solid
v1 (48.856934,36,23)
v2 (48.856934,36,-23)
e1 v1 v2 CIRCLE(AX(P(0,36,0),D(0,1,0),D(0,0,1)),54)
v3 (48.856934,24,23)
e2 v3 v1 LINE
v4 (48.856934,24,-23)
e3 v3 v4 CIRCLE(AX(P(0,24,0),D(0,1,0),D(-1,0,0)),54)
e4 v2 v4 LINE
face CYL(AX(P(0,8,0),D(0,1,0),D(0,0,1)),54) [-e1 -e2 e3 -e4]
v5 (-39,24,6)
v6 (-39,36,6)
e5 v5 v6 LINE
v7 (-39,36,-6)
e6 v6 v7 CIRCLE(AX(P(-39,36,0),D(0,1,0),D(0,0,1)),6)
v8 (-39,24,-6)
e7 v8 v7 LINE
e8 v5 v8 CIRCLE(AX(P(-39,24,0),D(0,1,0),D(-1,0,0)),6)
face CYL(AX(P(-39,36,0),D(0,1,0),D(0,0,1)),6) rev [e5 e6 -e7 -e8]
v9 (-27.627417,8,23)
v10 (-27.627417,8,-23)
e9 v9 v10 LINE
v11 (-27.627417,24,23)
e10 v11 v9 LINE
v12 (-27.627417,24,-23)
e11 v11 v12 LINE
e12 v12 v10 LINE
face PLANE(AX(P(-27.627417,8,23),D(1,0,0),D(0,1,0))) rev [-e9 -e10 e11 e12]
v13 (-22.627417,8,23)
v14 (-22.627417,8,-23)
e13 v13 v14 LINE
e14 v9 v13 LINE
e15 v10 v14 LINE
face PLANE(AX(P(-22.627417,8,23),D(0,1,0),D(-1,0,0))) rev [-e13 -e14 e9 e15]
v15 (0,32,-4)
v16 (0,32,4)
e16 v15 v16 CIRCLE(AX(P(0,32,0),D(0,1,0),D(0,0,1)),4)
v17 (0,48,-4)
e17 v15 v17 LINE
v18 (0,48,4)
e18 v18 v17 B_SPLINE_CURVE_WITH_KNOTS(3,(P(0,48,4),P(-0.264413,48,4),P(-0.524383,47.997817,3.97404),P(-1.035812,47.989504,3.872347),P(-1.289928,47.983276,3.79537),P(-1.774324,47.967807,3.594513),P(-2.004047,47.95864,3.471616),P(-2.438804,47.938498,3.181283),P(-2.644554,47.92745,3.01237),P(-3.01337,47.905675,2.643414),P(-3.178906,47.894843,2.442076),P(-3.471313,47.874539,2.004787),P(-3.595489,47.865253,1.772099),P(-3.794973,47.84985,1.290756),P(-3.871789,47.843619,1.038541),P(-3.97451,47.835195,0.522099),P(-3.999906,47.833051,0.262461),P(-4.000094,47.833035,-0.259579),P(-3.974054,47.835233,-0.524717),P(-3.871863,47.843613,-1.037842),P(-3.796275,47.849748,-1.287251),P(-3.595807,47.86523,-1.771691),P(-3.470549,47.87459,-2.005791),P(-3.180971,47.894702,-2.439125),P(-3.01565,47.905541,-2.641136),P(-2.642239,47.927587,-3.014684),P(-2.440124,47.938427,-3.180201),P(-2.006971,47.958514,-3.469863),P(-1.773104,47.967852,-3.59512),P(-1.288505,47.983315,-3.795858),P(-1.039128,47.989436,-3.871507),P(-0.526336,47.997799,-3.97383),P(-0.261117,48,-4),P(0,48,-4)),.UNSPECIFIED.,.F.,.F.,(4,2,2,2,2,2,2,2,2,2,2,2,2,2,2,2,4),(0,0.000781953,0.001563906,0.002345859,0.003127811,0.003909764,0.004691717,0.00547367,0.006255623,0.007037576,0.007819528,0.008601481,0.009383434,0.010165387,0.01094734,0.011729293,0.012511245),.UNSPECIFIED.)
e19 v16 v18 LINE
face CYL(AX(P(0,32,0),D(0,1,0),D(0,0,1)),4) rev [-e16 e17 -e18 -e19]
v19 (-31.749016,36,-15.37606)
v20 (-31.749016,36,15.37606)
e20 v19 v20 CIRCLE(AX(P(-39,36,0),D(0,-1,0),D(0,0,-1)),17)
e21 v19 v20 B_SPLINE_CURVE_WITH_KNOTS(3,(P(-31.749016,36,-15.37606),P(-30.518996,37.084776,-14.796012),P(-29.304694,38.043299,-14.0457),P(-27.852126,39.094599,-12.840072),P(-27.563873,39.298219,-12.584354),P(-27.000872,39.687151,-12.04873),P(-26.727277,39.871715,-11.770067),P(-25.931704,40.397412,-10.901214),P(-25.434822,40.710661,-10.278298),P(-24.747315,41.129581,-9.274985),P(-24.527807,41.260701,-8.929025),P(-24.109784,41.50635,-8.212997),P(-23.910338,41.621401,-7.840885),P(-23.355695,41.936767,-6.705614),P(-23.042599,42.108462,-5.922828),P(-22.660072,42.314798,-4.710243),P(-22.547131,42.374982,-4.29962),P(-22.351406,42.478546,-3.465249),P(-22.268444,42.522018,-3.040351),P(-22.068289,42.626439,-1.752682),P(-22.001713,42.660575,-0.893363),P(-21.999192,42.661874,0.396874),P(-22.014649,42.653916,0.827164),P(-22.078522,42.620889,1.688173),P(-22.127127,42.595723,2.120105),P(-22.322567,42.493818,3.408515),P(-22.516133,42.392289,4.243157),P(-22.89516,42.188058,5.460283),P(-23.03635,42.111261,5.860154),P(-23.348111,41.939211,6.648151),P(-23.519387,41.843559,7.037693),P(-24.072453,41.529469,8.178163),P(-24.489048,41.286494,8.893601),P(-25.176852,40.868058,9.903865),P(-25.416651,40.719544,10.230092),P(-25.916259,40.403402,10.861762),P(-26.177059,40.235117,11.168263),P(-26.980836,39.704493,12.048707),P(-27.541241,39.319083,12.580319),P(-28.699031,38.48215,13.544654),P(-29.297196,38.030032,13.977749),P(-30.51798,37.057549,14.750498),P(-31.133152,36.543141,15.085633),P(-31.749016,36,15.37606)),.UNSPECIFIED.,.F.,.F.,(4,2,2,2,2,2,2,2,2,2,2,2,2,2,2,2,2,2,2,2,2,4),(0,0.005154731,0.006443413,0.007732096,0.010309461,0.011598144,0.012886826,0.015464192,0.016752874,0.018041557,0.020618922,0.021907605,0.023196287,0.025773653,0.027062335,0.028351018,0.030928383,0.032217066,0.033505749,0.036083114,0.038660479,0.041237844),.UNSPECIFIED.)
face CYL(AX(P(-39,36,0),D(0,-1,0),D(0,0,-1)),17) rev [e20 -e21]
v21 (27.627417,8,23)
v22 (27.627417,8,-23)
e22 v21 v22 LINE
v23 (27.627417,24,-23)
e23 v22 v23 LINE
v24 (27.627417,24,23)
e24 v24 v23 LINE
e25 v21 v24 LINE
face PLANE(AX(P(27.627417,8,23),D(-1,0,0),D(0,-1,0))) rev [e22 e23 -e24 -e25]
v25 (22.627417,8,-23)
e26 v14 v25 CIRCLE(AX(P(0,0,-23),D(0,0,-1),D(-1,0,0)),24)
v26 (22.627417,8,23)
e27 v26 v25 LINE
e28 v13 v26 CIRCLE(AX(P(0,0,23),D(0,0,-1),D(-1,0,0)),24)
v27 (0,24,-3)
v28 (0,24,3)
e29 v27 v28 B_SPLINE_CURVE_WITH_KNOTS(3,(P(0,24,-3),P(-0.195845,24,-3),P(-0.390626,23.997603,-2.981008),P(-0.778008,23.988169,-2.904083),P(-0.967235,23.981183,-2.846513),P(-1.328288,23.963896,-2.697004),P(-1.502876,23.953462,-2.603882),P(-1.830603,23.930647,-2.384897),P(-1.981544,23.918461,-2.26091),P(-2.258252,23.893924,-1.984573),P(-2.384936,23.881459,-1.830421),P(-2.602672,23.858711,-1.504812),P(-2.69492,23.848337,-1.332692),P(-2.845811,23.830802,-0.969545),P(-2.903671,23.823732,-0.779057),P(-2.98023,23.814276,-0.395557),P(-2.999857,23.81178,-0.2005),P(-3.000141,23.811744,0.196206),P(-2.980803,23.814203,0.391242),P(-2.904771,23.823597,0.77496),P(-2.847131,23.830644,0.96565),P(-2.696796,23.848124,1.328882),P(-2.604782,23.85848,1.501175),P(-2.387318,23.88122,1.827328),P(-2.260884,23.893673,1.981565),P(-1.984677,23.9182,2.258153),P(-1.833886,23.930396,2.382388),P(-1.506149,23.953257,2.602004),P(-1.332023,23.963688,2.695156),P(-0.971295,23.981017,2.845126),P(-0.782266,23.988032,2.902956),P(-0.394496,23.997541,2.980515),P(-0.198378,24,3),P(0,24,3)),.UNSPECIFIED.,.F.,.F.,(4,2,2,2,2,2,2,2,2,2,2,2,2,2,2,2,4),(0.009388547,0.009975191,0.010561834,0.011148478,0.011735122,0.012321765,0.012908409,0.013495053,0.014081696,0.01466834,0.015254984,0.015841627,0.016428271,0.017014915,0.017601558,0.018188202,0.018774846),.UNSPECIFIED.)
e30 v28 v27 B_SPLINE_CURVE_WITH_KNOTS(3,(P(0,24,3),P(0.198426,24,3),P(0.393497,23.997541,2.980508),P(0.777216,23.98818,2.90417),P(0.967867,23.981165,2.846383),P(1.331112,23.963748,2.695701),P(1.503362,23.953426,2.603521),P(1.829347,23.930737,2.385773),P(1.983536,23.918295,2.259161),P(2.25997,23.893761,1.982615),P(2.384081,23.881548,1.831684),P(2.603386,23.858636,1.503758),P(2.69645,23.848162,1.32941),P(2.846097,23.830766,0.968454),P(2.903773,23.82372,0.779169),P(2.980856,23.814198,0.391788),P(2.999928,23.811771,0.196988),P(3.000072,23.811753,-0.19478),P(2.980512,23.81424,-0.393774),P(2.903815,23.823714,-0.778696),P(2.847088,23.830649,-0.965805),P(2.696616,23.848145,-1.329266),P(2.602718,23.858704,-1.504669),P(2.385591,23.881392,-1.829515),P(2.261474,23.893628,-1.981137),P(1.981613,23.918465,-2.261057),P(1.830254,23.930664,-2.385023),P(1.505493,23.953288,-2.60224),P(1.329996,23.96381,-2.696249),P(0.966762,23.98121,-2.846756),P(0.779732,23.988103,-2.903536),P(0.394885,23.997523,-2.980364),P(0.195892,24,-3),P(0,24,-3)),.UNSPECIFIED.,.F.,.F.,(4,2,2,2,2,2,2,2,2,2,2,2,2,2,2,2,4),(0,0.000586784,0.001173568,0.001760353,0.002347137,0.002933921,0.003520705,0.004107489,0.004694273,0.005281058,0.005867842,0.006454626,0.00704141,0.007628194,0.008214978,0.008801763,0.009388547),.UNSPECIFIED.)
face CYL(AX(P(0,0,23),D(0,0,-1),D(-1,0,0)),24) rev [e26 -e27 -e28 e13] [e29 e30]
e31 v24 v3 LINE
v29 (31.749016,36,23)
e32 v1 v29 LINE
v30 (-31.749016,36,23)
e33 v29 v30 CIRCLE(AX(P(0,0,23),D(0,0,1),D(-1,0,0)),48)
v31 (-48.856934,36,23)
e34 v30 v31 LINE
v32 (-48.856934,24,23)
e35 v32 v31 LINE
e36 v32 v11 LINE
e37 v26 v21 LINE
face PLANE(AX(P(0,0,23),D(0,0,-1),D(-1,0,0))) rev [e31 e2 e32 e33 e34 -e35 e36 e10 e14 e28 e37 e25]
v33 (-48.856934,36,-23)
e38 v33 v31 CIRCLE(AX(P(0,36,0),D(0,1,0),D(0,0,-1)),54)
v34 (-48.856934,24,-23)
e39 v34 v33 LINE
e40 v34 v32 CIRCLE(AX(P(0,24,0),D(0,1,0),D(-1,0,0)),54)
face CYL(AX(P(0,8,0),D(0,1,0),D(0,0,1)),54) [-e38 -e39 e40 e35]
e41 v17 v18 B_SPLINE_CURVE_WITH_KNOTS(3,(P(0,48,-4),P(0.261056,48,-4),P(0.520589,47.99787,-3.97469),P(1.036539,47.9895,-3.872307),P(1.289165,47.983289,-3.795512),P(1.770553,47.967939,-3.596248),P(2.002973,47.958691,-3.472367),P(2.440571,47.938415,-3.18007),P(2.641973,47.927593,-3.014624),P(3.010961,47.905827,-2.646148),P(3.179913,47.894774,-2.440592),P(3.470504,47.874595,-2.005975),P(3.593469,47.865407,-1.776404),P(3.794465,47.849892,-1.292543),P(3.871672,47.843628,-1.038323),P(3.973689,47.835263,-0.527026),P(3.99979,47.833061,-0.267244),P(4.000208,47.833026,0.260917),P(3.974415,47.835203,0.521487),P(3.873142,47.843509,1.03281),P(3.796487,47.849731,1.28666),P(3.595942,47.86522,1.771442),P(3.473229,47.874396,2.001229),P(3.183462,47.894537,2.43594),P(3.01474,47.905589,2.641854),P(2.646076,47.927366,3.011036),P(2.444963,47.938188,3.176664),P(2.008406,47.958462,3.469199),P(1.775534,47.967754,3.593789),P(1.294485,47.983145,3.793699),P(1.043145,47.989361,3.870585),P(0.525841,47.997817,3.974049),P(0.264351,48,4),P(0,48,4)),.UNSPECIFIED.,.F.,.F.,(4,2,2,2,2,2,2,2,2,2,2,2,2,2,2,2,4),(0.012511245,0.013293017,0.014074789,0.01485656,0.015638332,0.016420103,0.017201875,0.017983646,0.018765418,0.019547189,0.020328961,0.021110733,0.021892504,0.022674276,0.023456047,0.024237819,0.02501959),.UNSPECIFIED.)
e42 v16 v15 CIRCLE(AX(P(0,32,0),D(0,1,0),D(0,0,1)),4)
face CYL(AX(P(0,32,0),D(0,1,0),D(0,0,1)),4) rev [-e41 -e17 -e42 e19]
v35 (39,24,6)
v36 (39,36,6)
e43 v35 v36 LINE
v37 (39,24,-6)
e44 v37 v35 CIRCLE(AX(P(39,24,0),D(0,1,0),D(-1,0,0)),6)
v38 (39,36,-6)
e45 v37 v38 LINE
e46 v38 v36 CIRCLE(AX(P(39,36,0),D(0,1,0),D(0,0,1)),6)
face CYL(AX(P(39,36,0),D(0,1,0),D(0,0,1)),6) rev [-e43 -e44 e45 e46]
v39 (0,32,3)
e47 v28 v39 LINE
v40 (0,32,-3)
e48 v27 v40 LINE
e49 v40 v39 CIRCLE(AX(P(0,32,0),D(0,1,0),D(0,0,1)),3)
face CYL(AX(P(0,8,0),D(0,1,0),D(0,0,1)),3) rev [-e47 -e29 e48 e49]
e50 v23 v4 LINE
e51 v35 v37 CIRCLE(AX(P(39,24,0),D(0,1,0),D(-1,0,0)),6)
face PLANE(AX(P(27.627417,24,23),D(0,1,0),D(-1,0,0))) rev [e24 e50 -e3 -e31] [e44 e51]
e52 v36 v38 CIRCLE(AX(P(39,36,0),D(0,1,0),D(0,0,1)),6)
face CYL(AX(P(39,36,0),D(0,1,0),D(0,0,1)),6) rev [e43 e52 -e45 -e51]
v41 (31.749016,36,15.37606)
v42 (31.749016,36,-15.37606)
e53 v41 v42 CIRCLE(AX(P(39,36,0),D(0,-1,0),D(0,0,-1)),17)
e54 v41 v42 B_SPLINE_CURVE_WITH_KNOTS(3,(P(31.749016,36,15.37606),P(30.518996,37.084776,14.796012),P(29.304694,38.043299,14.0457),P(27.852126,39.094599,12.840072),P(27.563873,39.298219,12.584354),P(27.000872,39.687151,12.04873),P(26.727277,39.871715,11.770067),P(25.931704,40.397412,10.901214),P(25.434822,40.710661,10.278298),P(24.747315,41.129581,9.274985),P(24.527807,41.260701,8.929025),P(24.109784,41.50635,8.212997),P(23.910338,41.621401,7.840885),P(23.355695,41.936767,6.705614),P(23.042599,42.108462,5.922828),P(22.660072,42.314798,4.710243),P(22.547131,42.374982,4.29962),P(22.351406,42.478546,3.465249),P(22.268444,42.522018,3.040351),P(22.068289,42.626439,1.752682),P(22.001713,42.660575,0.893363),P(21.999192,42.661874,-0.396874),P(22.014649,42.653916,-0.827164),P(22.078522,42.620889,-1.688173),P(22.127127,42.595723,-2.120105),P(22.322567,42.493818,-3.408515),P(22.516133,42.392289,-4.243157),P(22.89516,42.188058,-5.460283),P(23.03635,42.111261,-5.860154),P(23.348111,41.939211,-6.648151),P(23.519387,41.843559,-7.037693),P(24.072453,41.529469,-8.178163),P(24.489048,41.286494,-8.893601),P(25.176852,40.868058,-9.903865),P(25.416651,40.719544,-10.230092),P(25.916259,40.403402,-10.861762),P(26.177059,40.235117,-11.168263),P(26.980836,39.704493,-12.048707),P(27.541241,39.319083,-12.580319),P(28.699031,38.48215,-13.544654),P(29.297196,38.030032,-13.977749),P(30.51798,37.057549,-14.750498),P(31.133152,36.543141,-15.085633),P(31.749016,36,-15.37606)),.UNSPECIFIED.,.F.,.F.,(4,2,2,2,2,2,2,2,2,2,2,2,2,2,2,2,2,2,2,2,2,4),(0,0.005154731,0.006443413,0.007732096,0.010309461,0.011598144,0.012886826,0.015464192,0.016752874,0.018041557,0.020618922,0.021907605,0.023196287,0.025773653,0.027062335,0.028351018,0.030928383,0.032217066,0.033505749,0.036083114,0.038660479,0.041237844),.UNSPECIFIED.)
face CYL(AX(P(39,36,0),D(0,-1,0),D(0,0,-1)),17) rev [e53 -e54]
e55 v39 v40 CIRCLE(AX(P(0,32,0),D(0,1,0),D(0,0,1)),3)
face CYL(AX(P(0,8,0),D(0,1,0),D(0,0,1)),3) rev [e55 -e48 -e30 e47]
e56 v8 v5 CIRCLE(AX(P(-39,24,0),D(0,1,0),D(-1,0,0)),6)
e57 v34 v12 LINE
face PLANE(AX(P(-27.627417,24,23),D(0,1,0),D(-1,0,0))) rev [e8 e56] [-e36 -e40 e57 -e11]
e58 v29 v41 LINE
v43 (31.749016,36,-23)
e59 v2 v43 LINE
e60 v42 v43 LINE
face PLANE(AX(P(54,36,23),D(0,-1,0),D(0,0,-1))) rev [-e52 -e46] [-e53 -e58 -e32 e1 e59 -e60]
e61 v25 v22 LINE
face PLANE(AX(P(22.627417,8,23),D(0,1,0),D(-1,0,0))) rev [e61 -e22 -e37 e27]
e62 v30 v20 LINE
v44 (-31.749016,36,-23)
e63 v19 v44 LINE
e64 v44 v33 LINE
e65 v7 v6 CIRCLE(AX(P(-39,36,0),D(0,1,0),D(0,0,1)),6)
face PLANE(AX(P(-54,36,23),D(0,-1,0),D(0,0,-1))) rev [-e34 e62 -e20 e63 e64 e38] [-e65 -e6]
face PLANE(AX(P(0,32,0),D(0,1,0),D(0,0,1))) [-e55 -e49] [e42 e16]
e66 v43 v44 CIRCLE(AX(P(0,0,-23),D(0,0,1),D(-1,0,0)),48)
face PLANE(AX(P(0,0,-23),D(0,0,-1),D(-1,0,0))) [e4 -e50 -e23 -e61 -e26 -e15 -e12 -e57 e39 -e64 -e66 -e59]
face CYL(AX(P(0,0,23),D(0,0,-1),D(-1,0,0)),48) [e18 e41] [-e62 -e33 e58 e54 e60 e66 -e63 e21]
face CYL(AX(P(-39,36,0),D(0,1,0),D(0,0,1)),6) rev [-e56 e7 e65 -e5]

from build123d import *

# Parameters (mm, degrees)
CAP_BODY_DEPTH               = 23
BOLT_HOLES_12_D              = 12
SKETCH7_W                    = 17
SKETCH7_H                    = 36
HOLE_34_AT_2_COUNT           = 2
HOLE_34_AT_2_PITCH           = 78
LUBE_COUNTERBORE_SKETCH_8_R  = 4
LUBE_COUNTERBORE_8_DEPTH     = 16
LUBE_HOLE_SKETCH_6_R         = 3
LUBE_HOLE_6_DEPTH            = 72.028163461
SIDE_RELIEF_SKETCH_OUTSIDE_W = 134.804
SIDE_RELIEF_SKETCH_OUTSIDE_H = 72.804
SIDE_RELIEF_CUT_DEPTH        = 66.03076203


with BuildPart() as part:
    # Cap Profile Sketch → Cap Body (new, symmetric)
    with BuildSketch(Plane.XY):
        with BuildLine():
            Line((-22.627416998, 8), (-27.627416998, 8))
            Line((-27.627416998, 8), (-27.627416998, 24))
            Line((-27.627416998, 24), (-54, 24))
            Line((-54, 24), (-54, 36))
            Line((-54, 36), (-31.749015733, 36))
            ThreePointArc((-31.749015733, 36), (0, 48), (31.749015733, 36))
            Line((31.749015733, 36), (54, 36))
            Line((54, 36), (54, 24))
            Line((54, 24), (27.627416998, 24))
            Line((27.627416998, 24), (27.627416998, 8))
            Line((27.627416998, 8), (22.627416998, 8))
            ThreePointArc((22.627416998, 8), (0, 24), (-22.627416998, 8))
        make_face()
    extrude(amount=CAP_BODY_DEPTH, both=True)

    # Bolt Holes Ø12 (through all)
    with Locations(Plane(origin=(0, 36, 0), x_dir=(1, 0, 0), z_dir=(0, 1, 0))):
        with Locations((-39, 0), (39, 0)):
            Hole(BOLT_HOLES_12_D / 2)

    # Sketch7 → Hole Ø34 (revolve, cut)
    with BuildSketch(Plane(origin=(-39, 36, 0), x_dir=(0, 0, -1), z_dir=(1, 0, 0))):
        with Locations((8.5, 18)):
            Rectangle(SKETCH7_W, SKETCH7_H)
    hole_34 = revolve(axis=Axis((-39, 29.65, 0), (0, 1, 0)), mode=Mode.SUBTRACT)

    # Hole Ø34 at 2: Hole Ø34 ×2
    with Locations(*[(i * HOLE_34_AT_2_PITCH, 0, 0) for i in range(1, HOLE_34_AT_2_COUNT)]):
        add(hole_34, mode=Mode.SUBTRACT)

    # Lube Counterbore Sketch Ø8 → Lube Counterbore Ø8 (cut)
    with BuildSketch(Plane(origin=(0, 48, 0), x_dir=(1, 0, 0), z_dir=(0, 1, 0))):
        with Locations(Location((0, 0, 0), (0, 0, 270))):
            Circle(LUBE_COUNTERBORE_SKETCH_8_R)
    extrude(amount=-LUBE_COUNTERBORE_8_DEPTH, mode=Mode.SUBTRACT)

    # Lube Hole Sketch Ø6 → Lube Hole Ø6 (cut, through all)
    with BuildSketch(Plane(origin=(0, 48, 0), x_dir=(1, 0, 0), z_dir=(0, 1, 0))):
        with Locations(Location((0, 0, 0), (0, 0, 270))):
            Circle(LUBE_HOLE_SKETCH_6_R)
    extrude(amount=-LUBE_HOLE_6_DEPTH, mode=Mode.SUBTRACT)

    # Side Relief Sketch outside → Side Relief Cut (cut, through all)
    with BuildSketch(Plane(origin=(0, 36, 0), x_dir=(1, 0, 0), z_dir=(0, 1, 0))):
        Rectangle(SIDE_RELIEF_SKETCH_OUTSIDE_W, SIDE_RELIEF_SKETCH_OUTSIDE_H)
        with BuildLine():
            Line((-31.749015733, 23), (31.749015733, 23))
            Line((31.749015733, 23), (48.856934001, 23))
            ThreePointArc((48.856934001, 23), (54, 0), (48.856934001, -23))
            Line((48.856934001, -23), (31.749015733, -23))
            Line((31.749015733, -23), (-31.749015733, -23))
            Line((-31.749015733, -23), (-48.856934001, -23))
            ThreePointArc((-48.856934001, -23), (-54, 0), (-48.856934001, 23))
            Line((-48.856934001, 23), (-31.749015733, 23))
        make_face(mode=Mode.SUBTRACT)
    extrude(amount=-SIDE_RELIEF_CUT_DEPTH, mode=Mode.SUBTRACT)


solid = part.part
